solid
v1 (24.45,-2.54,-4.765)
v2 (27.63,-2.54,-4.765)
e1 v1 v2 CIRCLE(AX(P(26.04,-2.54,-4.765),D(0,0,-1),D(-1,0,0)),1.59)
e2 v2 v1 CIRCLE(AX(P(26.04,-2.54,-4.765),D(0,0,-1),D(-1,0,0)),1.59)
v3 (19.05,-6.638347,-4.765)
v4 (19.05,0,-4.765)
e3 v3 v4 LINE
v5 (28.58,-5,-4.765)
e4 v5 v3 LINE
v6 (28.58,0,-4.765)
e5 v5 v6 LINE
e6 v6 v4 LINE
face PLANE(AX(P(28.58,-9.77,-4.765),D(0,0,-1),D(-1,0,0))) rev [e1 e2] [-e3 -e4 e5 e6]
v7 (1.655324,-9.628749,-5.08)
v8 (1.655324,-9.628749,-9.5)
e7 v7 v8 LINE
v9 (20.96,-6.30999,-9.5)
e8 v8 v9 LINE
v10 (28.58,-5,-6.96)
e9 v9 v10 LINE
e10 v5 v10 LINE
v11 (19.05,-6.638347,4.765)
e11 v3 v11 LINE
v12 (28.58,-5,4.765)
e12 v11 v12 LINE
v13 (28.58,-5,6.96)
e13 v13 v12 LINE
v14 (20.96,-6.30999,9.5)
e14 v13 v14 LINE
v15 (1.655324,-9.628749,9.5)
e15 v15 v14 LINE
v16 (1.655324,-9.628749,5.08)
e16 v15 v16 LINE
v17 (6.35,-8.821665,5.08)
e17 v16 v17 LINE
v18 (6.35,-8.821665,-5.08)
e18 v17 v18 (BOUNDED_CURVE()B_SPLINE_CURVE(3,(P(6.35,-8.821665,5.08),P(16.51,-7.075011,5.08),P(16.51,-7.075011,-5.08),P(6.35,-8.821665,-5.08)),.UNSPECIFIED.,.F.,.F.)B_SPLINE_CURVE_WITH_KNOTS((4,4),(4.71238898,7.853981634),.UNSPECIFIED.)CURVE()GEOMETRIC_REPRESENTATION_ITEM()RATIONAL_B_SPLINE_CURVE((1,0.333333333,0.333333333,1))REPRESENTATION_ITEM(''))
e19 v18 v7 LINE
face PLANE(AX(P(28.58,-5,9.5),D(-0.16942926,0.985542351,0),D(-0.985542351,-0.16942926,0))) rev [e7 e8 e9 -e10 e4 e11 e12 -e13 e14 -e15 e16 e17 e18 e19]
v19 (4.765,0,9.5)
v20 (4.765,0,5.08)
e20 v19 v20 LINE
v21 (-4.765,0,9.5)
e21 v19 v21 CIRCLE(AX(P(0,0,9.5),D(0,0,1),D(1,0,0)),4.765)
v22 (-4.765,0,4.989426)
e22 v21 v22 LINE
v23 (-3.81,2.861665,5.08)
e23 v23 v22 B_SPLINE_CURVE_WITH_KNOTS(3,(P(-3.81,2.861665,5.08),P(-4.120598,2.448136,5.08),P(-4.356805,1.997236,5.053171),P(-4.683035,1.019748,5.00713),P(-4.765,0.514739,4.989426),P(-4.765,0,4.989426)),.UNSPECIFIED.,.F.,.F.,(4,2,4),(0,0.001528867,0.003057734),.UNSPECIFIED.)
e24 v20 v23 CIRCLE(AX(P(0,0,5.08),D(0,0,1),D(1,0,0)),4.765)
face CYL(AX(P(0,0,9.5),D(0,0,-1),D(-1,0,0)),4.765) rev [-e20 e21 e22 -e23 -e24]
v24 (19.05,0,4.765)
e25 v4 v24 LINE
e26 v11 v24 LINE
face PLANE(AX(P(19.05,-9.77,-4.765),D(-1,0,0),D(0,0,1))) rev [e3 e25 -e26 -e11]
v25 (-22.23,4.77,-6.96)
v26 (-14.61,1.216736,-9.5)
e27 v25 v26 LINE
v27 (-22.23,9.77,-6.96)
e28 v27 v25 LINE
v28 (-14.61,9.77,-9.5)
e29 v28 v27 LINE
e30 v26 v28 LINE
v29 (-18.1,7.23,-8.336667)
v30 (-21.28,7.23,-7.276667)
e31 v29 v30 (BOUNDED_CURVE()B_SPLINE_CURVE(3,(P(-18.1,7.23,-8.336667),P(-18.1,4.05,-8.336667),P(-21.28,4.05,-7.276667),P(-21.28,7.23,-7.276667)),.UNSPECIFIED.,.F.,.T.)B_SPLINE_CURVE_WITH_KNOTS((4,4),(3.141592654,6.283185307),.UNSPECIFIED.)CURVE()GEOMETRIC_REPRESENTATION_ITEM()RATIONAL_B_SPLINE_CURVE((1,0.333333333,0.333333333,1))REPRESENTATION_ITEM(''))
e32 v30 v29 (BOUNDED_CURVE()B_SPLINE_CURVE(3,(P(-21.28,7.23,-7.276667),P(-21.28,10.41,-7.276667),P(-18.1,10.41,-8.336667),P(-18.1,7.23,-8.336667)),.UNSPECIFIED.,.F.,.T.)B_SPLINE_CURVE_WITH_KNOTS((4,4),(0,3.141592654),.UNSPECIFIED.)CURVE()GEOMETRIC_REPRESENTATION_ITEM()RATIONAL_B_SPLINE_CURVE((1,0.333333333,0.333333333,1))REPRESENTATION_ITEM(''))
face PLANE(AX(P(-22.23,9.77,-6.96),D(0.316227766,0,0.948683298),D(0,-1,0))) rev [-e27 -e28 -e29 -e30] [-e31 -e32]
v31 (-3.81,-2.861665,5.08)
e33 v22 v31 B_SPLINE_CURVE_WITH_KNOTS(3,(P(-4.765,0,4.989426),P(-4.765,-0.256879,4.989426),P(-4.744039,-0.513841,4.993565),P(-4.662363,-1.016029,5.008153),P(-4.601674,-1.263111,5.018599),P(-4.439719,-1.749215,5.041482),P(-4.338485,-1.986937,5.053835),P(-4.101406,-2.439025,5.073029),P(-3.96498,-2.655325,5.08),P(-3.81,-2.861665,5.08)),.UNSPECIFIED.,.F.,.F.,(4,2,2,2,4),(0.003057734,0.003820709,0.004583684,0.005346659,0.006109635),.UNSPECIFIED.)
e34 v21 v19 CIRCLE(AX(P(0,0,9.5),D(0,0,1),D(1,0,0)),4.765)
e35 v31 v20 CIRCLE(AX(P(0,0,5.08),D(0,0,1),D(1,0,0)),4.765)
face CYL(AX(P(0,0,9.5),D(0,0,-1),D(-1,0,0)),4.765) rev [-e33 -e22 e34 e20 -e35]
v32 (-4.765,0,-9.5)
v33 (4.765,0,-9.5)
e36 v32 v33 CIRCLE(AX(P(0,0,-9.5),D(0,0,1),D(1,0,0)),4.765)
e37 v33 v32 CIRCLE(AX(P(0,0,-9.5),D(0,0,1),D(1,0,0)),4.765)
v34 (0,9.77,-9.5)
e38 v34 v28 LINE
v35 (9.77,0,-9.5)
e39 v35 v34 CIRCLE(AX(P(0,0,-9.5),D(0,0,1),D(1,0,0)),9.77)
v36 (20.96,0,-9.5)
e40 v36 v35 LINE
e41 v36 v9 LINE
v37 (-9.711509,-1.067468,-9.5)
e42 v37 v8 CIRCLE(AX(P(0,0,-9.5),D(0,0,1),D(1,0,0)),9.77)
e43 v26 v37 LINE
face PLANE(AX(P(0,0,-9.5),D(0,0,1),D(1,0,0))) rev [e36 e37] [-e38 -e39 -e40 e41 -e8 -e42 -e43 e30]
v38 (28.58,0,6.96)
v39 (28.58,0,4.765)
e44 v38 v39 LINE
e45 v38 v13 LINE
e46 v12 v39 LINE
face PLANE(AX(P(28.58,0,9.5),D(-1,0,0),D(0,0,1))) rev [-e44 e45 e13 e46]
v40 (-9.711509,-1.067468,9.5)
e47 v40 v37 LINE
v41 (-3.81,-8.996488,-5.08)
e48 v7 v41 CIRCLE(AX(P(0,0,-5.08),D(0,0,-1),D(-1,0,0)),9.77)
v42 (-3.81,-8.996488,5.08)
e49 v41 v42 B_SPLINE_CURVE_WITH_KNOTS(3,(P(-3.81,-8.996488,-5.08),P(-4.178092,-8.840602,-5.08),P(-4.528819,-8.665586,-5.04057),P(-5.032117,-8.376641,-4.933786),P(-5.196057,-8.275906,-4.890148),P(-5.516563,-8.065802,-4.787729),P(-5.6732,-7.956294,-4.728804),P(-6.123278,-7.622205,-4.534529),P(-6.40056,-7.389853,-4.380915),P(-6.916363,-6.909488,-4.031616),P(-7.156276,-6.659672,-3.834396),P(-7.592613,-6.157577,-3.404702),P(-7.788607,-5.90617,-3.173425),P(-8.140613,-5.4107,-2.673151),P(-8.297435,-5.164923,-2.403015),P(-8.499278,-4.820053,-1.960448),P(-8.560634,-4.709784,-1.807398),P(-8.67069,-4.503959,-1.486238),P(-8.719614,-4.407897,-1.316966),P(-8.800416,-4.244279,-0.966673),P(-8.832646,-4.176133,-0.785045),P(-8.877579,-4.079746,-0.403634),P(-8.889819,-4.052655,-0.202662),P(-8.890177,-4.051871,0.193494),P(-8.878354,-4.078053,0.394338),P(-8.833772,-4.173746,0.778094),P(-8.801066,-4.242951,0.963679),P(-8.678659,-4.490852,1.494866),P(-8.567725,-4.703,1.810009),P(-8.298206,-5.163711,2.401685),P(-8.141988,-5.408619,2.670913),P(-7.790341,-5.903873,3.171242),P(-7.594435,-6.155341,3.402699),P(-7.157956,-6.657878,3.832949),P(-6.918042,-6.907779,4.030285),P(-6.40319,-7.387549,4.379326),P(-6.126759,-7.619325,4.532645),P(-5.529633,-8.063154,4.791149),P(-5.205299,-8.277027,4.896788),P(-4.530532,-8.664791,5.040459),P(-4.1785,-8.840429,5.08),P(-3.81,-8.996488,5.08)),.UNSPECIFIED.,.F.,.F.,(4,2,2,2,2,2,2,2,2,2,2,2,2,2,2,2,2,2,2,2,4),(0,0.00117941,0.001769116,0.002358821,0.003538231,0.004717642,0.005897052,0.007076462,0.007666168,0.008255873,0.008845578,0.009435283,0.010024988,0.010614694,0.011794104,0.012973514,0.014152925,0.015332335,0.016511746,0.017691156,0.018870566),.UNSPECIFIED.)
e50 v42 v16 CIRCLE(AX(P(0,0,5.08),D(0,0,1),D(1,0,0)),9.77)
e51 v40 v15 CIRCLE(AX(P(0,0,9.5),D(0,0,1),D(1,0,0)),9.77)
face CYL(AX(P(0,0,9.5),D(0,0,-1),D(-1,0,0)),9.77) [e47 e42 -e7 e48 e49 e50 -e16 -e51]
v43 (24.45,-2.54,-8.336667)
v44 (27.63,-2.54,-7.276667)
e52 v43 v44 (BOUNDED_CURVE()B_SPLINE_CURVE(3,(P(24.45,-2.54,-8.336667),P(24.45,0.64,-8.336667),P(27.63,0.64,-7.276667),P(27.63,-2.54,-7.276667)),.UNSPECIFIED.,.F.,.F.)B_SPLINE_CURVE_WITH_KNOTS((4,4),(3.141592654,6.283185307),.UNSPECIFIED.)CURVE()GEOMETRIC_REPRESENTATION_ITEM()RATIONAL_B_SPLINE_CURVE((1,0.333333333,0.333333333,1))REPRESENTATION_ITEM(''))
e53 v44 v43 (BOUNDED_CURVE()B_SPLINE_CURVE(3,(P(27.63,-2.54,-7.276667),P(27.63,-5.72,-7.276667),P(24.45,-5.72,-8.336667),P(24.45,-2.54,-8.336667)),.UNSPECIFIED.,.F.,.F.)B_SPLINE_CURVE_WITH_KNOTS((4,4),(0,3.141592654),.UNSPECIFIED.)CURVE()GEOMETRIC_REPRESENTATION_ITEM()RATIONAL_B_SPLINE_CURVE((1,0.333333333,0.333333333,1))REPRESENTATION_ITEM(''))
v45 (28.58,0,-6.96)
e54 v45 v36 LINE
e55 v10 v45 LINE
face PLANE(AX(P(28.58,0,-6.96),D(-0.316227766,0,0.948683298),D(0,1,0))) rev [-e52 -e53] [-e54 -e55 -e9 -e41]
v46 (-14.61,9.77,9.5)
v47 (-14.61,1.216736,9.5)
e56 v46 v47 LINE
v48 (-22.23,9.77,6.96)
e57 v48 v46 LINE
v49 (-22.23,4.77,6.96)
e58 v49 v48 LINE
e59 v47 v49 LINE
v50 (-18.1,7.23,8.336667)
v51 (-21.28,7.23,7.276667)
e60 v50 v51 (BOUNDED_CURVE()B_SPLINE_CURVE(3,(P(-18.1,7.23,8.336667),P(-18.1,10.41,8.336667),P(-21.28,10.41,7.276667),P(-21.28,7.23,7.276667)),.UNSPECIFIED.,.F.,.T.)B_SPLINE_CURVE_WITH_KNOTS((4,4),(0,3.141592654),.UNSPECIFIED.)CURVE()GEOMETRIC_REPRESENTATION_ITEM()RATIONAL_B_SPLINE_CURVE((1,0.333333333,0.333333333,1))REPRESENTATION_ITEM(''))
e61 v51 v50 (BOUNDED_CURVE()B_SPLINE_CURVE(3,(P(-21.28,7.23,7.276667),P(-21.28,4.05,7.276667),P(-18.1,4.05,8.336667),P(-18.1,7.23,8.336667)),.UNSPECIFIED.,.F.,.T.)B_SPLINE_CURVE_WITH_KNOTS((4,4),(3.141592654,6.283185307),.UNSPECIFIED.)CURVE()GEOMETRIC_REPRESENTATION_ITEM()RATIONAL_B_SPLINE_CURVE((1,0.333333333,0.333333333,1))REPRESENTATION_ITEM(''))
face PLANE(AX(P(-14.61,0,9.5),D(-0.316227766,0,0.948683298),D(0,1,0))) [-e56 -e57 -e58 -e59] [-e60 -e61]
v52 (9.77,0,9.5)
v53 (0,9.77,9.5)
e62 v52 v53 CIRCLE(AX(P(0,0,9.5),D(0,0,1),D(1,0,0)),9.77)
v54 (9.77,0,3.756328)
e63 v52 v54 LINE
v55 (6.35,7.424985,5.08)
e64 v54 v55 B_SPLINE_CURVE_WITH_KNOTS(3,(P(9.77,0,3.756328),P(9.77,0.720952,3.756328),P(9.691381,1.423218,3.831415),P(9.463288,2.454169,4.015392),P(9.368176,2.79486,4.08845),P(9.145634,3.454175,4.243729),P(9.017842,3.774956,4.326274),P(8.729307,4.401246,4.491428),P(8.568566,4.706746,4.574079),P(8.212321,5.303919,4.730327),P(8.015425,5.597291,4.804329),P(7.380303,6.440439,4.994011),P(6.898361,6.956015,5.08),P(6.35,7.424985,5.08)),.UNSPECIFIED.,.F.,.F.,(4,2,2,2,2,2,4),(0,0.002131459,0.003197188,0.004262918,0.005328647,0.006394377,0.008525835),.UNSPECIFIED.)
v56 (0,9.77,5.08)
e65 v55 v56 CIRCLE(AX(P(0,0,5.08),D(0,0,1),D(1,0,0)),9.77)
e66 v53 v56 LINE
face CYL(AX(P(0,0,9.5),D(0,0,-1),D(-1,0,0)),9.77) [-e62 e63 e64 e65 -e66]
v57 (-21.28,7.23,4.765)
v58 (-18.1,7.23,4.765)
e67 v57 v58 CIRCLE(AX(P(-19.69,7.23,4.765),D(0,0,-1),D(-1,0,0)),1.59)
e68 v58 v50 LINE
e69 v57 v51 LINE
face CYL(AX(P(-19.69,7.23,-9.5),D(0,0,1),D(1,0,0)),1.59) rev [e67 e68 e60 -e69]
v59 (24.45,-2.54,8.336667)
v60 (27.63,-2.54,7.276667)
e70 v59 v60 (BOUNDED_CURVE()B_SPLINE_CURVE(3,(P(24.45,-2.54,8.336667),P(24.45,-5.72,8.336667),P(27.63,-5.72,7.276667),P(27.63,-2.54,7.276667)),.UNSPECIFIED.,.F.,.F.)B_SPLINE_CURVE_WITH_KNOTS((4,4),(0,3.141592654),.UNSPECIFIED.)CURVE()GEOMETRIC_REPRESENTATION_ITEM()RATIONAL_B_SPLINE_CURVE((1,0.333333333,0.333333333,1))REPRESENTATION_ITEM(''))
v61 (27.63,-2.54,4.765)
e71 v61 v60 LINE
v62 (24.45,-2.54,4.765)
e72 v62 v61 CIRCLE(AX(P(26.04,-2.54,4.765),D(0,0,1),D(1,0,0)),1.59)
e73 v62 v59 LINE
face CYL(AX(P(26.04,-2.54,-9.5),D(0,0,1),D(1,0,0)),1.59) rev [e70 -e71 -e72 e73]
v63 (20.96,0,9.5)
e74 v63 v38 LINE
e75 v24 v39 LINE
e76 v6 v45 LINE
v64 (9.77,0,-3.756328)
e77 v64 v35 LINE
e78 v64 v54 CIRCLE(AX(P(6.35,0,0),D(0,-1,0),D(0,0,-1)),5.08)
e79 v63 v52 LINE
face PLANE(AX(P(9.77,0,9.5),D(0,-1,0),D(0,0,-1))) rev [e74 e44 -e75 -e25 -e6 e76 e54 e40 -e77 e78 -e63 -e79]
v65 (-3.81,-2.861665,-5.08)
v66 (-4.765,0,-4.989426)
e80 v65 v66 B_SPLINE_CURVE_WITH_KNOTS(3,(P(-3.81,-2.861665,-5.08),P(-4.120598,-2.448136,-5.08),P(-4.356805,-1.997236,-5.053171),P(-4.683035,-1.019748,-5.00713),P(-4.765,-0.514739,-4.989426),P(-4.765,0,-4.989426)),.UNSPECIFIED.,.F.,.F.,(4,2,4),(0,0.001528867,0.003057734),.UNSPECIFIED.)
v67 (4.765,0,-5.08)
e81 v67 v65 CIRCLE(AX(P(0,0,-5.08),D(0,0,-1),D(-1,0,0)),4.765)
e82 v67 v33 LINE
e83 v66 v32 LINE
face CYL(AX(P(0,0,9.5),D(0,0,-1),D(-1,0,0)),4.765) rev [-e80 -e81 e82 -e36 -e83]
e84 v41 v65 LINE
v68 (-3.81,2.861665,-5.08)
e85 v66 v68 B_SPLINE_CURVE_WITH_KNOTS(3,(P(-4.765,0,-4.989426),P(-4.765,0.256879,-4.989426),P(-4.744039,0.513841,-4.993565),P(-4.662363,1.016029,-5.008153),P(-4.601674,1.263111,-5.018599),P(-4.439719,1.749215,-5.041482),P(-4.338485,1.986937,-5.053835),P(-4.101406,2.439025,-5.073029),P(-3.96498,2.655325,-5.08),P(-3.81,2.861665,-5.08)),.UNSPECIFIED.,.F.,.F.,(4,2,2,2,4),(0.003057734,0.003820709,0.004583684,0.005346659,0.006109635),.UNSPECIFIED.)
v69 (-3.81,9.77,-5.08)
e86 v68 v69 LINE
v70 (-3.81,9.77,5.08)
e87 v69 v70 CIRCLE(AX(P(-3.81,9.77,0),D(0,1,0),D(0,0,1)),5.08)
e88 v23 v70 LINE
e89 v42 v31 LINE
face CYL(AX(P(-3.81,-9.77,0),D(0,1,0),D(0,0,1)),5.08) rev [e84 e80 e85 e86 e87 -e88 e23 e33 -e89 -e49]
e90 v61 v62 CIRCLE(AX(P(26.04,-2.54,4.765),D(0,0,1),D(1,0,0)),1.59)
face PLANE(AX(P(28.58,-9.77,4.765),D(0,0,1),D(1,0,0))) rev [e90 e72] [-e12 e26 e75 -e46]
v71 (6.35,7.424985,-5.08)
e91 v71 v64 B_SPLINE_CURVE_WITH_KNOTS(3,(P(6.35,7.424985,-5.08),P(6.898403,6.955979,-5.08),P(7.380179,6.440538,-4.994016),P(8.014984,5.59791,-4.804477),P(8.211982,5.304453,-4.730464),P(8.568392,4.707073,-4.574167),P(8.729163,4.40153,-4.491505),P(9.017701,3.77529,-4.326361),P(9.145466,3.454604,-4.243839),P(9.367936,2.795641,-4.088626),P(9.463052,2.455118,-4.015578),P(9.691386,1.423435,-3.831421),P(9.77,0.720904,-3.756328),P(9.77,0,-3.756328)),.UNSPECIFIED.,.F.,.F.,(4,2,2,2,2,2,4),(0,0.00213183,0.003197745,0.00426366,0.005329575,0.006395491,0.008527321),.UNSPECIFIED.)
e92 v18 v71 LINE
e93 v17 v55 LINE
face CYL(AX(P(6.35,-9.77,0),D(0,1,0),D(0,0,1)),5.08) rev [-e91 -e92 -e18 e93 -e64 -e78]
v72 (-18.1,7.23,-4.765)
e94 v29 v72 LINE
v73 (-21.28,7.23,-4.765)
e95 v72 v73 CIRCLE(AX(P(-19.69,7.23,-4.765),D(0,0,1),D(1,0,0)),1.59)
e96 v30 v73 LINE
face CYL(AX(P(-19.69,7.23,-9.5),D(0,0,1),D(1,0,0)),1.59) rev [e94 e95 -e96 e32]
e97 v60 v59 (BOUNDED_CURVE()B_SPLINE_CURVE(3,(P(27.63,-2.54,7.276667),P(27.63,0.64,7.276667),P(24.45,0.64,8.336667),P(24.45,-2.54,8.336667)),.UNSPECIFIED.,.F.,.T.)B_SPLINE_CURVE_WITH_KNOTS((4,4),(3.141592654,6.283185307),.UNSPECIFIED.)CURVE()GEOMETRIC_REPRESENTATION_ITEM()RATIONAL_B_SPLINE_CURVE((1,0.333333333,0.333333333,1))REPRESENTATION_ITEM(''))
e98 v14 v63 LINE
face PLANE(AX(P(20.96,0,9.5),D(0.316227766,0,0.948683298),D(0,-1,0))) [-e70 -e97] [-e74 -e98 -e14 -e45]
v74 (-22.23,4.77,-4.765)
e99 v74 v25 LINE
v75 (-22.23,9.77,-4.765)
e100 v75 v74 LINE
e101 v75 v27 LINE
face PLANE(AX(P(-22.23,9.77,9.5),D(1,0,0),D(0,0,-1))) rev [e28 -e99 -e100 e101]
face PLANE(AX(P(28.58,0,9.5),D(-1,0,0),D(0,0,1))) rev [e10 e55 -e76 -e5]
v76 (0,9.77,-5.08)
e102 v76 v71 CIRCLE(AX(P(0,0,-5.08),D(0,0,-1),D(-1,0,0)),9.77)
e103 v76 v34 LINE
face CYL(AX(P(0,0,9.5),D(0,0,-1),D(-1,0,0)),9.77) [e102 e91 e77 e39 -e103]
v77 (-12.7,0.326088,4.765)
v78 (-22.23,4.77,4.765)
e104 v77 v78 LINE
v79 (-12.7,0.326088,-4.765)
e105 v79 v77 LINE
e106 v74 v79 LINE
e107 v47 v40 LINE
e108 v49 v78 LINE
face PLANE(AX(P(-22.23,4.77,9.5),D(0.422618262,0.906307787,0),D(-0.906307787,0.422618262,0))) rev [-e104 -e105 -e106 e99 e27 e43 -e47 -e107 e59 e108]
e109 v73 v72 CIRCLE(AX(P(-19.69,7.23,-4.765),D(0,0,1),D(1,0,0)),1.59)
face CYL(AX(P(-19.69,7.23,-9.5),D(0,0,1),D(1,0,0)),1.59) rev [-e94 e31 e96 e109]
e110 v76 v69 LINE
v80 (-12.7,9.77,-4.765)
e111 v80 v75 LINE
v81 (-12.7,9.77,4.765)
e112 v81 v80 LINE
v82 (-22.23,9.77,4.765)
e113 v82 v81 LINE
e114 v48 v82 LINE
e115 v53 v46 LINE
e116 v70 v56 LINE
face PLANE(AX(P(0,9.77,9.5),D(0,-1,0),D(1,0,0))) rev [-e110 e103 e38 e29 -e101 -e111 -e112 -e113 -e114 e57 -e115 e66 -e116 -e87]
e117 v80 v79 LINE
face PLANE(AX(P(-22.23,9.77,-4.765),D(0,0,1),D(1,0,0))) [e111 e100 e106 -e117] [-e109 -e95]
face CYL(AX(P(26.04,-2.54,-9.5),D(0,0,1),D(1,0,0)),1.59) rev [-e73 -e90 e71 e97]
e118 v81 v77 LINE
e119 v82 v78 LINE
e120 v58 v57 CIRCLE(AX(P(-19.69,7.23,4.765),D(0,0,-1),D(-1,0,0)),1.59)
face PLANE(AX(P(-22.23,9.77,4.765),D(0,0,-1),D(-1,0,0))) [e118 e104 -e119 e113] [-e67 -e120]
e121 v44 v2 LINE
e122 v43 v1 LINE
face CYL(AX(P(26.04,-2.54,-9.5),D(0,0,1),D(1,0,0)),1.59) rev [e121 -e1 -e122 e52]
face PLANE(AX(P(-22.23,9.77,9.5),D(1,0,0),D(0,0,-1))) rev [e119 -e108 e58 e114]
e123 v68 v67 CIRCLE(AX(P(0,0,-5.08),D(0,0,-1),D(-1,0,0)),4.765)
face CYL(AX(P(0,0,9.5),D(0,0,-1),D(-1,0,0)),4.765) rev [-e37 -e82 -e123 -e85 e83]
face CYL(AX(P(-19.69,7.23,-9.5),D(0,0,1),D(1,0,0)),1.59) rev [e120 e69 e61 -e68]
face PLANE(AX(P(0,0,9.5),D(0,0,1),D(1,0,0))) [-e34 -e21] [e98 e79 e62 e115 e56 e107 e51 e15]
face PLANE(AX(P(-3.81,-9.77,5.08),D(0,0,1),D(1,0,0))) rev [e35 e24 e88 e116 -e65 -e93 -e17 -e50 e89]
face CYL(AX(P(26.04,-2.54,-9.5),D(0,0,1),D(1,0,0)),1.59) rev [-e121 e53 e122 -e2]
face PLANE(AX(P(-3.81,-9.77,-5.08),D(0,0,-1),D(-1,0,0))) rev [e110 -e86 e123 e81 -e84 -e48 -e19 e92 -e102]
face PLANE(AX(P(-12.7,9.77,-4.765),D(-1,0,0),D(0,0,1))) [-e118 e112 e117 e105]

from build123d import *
from OCP.BRepFilletAPI import BRepFilletAPI_MakeChamfer

# Parameters (mm, degrees)
ROCKER_BODY_PROFILE_SKETCH_R      = 4.765
ROCKER_BODY_DEPTH                 = 9.5
ARM_END_CHAMFER_A_SIZE            = 7.62
ARM_END_CHAMFER_A_SIZE2           = 2.54
ARM_END_CHAMFER_B_SIZE            = 2.54
ARM_END_CHAMFER_B_SIZE2           = 7.62
FORK_SLOTS_SKETCH_W               = 9.53
FORK_SLOTS_SKETCH_H               = 9.53
FORK_SLOT_CUT_A_DEPTH             = 32.662585176
FORK_SLOT_CUT_B_DEPTH             = 32.662585176
FORK_SLOT_CUT_B_DEPTH_BACK        = 32.662585176
SKETCH2_2_W                       = 9.53
SKETCH2_2_H                       = 9.53
CENTRE_POCKET_DEPTH               = 32.662585176
CENTRE_POCKET_DEPTH_BACK          = 32.662585176
FORK_PIN_HOLES_2X_3_18_DEPTH      = 32.662585236
FORK_PIN_HOLES_2X_3_18_DEPTH_BACK = 32.662585236
FORK_PIN_HOLES_SKETCH_R           = 1.59


with BuildPart() as part:
    # Rocker Body Profile Sketch → Rocker Body (new, symmetric)
    with BuildSketch(Plane.XY):
        with BuildLine():
            Line((0, 9.77), (-22.23, 9.77))
            Line((-22.23, 9.77), (-22.23, 4.77))
            Line((-22.23, 4.77), (-9.711509246, -1.067468107))
            ThreePointArc((-9.711509246, -1.067468107), (-5.877874817, -7.804068659), (1.655323868, -9.628748771))
            Line((1.655323868, -9.628748771), (28.58, -5))
            Line((28.58, -5), (28.58, 0))
            Line((28.58, 0), (9.77, 0))
            ThreePointArc((9.77, 0), (6.908433252, 6.908433252), (0, 9.77))
        make_face()
        Circle(ROCKER_BODY_PROFILE_SKETCH_R, mode=Mode.SUBTRACT)
    extrude(amount=ROCKER_BODY_DEPTH, both=True)

    # Arm End Chamfer A
    arm_end_chamfer_a_edges = [part.edges().sort_by_distance(p)[0] for p in [
        (-22.23, 7.27, -9.5),
        (28.58, -2.5, -9.5),
    ]]
    arm_end_chamfer_a_side = [part.faces().sort_by_distance(p)[0] for p in [
        (-11.115, 9.225622585, -9.5),
    ]]
    chamfer(arm_end_chamfer_a_edges, length=ARM_END_CHAMFER_A_SIZE, length2=ARM_END_CHAMFER_A_SIZE2, reference=arm_end_chamfer_a_side[0])

    # Arm End Chamfer B: one chamfer whose edges measure the first distance from different faces: ONE call of the kernel's chamfer builder (chamfer() names one face for all edges)
    arm_end_chamfer_b_edges_1 = [part.edges().sort_by_distance(p)[0] for p in [
        (-22.23, 7.27, 9.5),
    ]]
    arm_end_chamfer_b_side_1 = [part.faces().sort_by_distance(p)[0] for p in [
        (-22.23, 7.27, 1.27),
    ]]
    arm_end_chamfer_b_edges_2 = [part.edges().sort_by_distance(p)[0] for p in [
        (28.58, -2.5, 9.5),
    ]]
    arm_end_chamfer_b_side_2 = [part.faces().sort_by_distance(p)[0] for p in [
        (28.58, -2.5, 1.27),
    ]]
    arm_end_chamfer_b = BRepFilletAPI_MakeChamfer(part.part.solid().wrapped)
    for e in arm_end_chamfer_b_edges_1:
        arm_end_chamfer_b.Add(ARM_END_CHAMFER_B_SIZE, ARM_END_CHAMFER_B_SIZE2, e.wrapped, arm_end_chamfer_b_side_1[0].wrapped)  # the first distance lies on this face
    for e in arm_end_chamfer_b_edges_2:
        arm_end_chamfer_b.Add(ARM_END_CHAMFER_B_SIZE, ARM_END_CHAMFER_B_SIZE2, e.wrapped, arm_end_chamfer_b_side_2[0].wrapped)  # the first distance lies on this face
    add(Compound.cast(arm_end_chamfer_b.Shape()), mode=Mode.REPLACE)

    # Fork Slots Sketch → Fork Slot Cut A (cut, through all)
    with BuildSketch(Plane(origin=(0, 0, 0), x_dir=(1, 0, 0), z_dir=(0, 1, 0))):
        with Locations((-17.465, 0)):
            Rectangle(FORK_SLOTS_SKETCH_W, FORK_SLOTS_SKETCH_H)
        with Locations((23.815, 0)):
            Rectangle(FORK_SLOTS_SKETCH_W, FORK_SLOTS_SKETCH_H)
    extrude(amount=-FORK_SLOT_CUT_A_DEPTH, mode=Mode.SUBTRACT)

    # Sketch2_2 → Fork Slot Cut B (cut, two sides: drawn at the far end of the back side and taken through both)
    with BuildSketch(Plane(origin=(0, 0, 0), x_dir=(1, 0, 0), z_dir=(0, 1, 0)).offset(-FORK_SLOT_CUT_B_DEPTH_BACK)):
        with Locations((-17.465, 0)):
            Rectangle(SKETCH2_2_W, SKETCH2_2_H)
        with Locations((23.815, 0)):
            Rectangle(SKETCH2_2_W, SKETCH2_2_H)
    extrude(amount=FORK_SLOT_CUT_B_DEPTH + FORK_SLOT_CUT_B_DEPTH_BACK, mode=Mode.SUBTRACT)

    # Centre Pocket Sketch → Centre Pocket (cut, two sides: drawn at the far end of the back side and taken through both)
    with BuildSketch(Plane(origin=(0, 0, 0), x_dir=(1, 0, 0), z_dir=(0, 1, 0)).offset(-CENTRE_POCKET_DEPTH_BACK)):
        with BuildLine():
            Line((-3.81, 5.08), (6.35, 5.08))
            ThreePointArc((6.35, 5.08), (11.43, 0), (6.35, -5.08))
            Line((6.35, -5.08), (-3.81, -5.08))
            ThreePointArc((-3.81, -5.08), (-8.89, 0), (-3.81, 5.08))
        make_face()
    extrude(amount=CENTRE_POCKET_DEPTH + CENTRE_POCKET_DEPTH_BACK, mode=Mode.SUBTRACT)

    # Fork Pin Holes Sketch → Fork Pin Holes 2x_3.18 (cut, two sides: drawn at the far end of the back side and taken through both)
    with BuildSketch(Plane.XY.offset(-FORK_PIN_HOLES_2X_3_18_DEPTH_BACK)):
        with Locations((-19.69, 7.23)):
            Circle(FORK_PIN_HOLES_SKETCH_R)
        with Locations((26.04, -2.54)):
            Circle(FORK_PIN_HOLES_SKETCH_R)
    extrude(amount=FORK_PIN_HOLES_2X_3_18_DEPTH + FORK_PIN_HOLES_2X_3_18_DEPTH_BACK, mode=Mode.SUBTRACT)


solid = part.part
